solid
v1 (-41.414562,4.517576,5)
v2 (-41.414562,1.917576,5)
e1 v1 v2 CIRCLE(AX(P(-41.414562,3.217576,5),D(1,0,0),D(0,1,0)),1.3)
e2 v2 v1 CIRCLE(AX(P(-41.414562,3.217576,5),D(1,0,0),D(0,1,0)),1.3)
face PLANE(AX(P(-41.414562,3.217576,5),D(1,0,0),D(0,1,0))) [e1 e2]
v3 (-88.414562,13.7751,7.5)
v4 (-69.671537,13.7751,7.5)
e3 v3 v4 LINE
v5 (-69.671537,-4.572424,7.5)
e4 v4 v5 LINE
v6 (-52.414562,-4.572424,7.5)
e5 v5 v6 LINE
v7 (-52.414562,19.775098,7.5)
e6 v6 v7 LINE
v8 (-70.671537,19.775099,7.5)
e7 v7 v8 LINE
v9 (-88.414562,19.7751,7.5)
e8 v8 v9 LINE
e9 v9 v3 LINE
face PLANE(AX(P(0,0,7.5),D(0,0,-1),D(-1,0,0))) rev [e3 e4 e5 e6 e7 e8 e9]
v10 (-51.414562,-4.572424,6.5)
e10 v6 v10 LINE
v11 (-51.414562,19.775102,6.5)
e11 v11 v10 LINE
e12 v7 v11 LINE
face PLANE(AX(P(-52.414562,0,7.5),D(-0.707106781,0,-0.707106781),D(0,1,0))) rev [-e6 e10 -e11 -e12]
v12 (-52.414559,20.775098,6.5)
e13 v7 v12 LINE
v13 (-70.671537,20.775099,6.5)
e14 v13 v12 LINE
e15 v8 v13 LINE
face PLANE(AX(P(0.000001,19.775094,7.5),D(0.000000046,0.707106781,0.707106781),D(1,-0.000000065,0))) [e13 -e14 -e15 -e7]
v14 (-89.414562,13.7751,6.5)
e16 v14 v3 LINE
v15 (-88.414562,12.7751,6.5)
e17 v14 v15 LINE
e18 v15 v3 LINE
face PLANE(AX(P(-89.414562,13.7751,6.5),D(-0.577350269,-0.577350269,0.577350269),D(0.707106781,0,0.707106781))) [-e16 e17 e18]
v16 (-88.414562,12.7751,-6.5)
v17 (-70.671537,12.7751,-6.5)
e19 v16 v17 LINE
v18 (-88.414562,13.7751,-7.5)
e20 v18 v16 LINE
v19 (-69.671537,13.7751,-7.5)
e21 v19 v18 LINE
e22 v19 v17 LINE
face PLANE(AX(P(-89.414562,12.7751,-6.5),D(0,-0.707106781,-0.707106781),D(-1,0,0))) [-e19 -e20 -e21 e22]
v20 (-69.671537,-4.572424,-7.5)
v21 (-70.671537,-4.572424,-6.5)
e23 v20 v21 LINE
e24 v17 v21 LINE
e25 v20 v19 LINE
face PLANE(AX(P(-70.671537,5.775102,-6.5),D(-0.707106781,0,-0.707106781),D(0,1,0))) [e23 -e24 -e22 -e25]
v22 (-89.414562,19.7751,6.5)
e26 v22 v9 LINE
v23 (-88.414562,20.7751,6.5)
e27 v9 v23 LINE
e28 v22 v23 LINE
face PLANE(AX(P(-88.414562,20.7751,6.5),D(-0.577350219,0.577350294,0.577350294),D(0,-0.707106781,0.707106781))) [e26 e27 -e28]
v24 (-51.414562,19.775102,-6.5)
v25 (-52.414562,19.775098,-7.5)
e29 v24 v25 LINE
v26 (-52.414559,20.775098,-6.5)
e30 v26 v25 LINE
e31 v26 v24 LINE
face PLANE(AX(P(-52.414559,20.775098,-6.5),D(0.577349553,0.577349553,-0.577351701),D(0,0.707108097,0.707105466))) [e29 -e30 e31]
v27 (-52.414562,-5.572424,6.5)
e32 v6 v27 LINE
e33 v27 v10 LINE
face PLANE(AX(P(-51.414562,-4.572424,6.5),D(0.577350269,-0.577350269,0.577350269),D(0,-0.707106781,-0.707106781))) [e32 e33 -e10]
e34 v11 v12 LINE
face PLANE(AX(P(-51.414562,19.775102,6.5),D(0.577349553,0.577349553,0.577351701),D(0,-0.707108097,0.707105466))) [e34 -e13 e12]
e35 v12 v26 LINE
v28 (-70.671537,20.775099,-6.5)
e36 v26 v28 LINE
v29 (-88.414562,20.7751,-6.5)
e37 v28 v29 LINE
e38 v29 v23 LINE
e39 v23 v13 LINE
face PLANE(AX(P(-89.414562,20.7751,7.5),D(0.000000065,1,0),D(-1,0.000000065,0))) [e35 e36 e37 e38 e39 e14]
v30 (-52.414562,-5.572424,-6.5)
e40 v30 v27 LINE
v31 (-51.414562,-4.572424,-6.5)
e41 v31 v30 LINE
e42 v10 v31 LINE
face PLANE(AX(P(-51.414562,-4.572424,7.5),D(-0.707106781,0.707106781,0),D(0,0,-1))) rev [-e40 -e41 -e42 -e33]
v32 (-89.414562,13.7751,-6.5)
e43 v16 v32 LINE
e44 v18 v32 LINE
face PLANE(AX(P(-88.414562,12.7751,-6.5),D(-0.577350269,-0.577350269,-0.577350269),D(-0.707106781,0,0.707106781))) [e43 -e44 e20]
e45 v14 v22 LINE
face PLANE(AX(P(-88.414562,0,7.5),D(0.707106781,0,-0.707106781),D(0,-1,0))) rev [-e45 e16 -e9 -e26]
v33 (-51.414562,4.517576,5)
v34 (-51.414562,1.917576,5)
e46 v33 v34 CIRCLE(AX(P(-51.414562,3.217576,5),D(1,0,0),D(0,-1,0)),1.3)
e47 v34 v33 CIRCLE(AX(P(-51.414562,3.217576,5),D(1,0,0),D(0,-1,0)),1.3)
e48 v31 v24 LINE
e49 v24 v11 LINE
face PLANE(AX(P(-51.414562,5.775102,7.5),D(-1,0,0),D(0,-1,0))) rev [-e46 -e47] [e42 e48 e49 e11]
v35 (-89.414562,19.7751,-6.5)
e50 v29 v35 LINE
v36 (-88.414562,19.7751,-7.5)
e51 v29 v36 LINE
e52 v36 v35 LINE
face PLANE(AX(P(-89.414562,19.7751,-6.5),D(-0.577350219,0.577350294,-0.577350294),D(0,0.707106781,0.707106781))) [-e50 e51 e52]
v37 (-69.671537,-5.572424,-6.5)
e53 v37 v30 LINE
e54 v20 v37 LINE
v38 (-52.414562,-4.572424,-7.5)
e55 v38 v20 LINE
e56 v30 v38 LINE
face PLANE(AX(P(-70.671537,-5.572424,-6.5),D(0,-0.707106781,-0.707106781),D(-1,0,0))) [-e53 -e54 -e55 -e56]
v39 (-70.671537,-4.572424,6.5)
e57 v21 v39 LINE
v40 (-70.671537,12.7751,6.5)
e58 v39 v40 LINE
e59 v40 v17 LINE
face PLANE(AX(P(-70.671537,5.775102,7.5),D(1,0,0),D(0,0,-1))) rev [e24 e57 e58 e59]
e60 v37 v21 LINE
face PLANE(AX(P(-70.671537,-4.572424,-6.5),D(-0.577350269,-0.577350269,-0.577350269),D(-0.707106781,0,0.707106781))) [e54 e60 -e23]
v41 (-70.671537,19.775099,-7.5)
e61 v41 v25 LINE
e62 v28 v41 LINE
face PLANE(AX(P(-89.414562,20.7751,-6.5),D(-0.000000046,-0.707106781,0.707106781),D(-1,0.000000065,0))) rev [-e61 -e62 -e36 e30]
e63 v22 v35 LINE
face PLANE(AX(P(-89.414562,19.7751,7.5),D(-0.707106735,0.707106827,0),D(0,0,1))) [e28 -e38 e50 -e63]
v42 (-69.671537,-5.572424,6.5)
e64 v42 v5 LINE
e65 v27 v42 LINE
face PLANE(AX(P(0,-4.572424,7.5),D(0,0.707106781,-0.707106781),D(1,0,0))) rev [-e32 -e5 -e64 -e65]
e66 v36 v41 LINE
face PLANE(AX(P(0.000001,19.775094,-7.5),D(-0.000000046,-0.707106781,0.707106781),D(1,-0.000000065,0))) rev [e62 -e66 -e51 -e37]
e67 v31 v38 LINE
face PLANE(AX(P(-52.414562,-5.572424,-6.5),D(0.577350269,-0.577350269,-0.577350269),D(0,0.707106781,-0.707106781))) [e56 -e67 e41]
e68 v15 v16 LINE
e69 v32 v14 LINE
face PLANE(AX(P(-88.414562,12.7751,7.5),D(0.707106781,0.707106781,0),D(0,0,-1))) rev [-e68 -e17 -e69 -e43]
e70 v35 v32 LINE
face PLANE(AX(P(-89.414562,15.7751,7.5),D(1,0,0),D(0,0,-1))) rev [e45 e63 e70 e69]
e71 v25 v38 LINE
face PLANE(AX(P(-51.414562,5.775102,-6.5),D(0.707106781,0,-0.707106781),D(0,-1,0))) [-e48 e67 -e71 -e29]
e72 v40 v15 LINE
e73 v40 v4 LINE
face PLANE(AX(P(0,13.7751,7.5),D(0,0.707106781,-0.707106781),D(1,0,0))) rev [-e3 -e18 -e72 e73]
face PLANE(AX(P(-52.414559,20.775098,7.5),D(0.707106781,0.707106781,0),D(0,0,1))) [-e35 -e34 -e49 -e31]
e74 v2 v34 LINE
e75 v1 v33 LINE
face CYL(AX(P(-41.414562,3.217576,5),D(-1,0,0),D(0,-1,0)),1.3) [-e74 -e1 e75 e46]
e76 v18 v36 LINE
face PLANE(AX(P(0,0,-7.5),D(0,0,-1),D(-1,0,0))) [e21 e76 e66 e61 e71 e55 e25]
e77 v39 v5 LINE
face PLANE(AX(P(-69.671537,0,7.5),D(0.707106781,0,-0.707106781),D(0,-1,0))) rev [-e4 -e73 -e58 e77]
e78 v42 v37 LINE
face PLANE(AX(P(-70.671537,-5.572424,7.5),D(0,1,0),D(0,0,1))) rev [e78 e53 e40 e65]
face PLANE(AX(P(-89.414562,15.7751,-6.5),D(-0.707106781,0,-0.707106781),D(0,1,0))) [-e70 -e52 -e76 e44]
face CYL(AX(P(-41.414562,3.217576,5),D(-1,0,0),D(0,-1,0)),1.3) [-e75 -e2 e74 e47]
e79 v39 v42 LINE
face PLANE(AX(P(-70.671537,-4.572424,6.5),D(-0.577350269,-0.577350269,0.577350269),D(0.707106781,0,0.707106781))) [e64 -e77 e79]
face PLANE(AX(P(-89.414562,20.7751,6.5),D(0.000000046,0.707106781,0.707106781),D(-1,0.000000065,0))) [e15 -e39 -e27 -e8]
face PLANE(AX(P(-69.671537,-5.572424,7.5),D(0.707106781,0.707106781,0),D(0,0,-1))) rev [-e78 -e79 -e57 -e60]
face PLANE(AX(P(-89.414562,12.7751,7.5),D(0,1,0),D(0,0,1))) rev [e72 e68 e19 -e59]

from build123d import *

# Parameters (mm, degrees)
BOSS_EXTRUDE1_DEPTH = 7.5
SKETCH3_R           = 1.3
BOSS_EXTRUDE2_DEPTH = 10
CHAMFER1_SIZE       = 1


with BuildPart() as part:
    # Model → Boss-Extrude1 (new, symmetric)
    with BuildSketch(Plane.XY):
        Polygon((-51.414562431, 5.775101607), (-51.414562431, 20.775101607), (-70.671536853, 20.775099073), (-89.414562431, 20.775100292), (-89.414562431, 15.775100292), (-89.414562431, 12.775100292), (-70.671536853, 12.775100292), (-70.671536853, 5.775101607), (-70.671536853, -5.572423542), (-51.414562431, -5.572423542), align=None)
    extrude(amount=BOSS_EXTRUDE1_DEPTH, both=True)

    # Sketch3 → Boss-Extrude2 (add)
    with BuildSketch(Plane(origin=(-51.414562431, 0, 0), x_dir=(0, 0, -1), z_dir=(1, 0, 0))):
        with Locations(Location((-5, 3.217576458, 0), (0, 0, 270))):
            Circle(SKETCH3_R)
    extrude(amount=BOSS_EXTRUDE2_DEPTH)

    # Chamfer1
    chamfer1_edges = [part.edges().sort_by_distance(p)[0] for p in [
        (-80.043049642, 20.775099682, -7.5),
        (-61.043049642, 20.77510034, -7.5),
        (-51.414562431, 7.601339033, -7.5),
        (-61.043049642, -5.572423542, -7.5),
        (-70.671536853, 3.601338375, -7.5),
        (-80.043049642, 12.775100292, -7.5),
        (-61.043049642, -5.572423542, 7.5),
        (-51.414562431, 7.601339033, 7.5),
        (-89.414562431, 12.775100292, 0),
        (-89.414562431, 20.775100292, 0),
        (-51.414562431, 20.775101607, 0),
        (-51.414562431, -5.572423542, 0),
        (-70.671536853, -5.572423542, 0),
        (-61.043049642, 20.77510034, 7.5),
        (-80.043049642, 20.775099682, 7.5),
        (-89.414562431, 16.775100292, 7.5),
        (-80.043049642, 12.775100292, 7.5),
        (-70.671536853, 3.601338375, 7.5),
        (-89.414562431, 16.775100292, -7.5),
    ]]
    chamfer(chamfer1_edges, length=CHAMFER1_SIZE)


solid = part.part
